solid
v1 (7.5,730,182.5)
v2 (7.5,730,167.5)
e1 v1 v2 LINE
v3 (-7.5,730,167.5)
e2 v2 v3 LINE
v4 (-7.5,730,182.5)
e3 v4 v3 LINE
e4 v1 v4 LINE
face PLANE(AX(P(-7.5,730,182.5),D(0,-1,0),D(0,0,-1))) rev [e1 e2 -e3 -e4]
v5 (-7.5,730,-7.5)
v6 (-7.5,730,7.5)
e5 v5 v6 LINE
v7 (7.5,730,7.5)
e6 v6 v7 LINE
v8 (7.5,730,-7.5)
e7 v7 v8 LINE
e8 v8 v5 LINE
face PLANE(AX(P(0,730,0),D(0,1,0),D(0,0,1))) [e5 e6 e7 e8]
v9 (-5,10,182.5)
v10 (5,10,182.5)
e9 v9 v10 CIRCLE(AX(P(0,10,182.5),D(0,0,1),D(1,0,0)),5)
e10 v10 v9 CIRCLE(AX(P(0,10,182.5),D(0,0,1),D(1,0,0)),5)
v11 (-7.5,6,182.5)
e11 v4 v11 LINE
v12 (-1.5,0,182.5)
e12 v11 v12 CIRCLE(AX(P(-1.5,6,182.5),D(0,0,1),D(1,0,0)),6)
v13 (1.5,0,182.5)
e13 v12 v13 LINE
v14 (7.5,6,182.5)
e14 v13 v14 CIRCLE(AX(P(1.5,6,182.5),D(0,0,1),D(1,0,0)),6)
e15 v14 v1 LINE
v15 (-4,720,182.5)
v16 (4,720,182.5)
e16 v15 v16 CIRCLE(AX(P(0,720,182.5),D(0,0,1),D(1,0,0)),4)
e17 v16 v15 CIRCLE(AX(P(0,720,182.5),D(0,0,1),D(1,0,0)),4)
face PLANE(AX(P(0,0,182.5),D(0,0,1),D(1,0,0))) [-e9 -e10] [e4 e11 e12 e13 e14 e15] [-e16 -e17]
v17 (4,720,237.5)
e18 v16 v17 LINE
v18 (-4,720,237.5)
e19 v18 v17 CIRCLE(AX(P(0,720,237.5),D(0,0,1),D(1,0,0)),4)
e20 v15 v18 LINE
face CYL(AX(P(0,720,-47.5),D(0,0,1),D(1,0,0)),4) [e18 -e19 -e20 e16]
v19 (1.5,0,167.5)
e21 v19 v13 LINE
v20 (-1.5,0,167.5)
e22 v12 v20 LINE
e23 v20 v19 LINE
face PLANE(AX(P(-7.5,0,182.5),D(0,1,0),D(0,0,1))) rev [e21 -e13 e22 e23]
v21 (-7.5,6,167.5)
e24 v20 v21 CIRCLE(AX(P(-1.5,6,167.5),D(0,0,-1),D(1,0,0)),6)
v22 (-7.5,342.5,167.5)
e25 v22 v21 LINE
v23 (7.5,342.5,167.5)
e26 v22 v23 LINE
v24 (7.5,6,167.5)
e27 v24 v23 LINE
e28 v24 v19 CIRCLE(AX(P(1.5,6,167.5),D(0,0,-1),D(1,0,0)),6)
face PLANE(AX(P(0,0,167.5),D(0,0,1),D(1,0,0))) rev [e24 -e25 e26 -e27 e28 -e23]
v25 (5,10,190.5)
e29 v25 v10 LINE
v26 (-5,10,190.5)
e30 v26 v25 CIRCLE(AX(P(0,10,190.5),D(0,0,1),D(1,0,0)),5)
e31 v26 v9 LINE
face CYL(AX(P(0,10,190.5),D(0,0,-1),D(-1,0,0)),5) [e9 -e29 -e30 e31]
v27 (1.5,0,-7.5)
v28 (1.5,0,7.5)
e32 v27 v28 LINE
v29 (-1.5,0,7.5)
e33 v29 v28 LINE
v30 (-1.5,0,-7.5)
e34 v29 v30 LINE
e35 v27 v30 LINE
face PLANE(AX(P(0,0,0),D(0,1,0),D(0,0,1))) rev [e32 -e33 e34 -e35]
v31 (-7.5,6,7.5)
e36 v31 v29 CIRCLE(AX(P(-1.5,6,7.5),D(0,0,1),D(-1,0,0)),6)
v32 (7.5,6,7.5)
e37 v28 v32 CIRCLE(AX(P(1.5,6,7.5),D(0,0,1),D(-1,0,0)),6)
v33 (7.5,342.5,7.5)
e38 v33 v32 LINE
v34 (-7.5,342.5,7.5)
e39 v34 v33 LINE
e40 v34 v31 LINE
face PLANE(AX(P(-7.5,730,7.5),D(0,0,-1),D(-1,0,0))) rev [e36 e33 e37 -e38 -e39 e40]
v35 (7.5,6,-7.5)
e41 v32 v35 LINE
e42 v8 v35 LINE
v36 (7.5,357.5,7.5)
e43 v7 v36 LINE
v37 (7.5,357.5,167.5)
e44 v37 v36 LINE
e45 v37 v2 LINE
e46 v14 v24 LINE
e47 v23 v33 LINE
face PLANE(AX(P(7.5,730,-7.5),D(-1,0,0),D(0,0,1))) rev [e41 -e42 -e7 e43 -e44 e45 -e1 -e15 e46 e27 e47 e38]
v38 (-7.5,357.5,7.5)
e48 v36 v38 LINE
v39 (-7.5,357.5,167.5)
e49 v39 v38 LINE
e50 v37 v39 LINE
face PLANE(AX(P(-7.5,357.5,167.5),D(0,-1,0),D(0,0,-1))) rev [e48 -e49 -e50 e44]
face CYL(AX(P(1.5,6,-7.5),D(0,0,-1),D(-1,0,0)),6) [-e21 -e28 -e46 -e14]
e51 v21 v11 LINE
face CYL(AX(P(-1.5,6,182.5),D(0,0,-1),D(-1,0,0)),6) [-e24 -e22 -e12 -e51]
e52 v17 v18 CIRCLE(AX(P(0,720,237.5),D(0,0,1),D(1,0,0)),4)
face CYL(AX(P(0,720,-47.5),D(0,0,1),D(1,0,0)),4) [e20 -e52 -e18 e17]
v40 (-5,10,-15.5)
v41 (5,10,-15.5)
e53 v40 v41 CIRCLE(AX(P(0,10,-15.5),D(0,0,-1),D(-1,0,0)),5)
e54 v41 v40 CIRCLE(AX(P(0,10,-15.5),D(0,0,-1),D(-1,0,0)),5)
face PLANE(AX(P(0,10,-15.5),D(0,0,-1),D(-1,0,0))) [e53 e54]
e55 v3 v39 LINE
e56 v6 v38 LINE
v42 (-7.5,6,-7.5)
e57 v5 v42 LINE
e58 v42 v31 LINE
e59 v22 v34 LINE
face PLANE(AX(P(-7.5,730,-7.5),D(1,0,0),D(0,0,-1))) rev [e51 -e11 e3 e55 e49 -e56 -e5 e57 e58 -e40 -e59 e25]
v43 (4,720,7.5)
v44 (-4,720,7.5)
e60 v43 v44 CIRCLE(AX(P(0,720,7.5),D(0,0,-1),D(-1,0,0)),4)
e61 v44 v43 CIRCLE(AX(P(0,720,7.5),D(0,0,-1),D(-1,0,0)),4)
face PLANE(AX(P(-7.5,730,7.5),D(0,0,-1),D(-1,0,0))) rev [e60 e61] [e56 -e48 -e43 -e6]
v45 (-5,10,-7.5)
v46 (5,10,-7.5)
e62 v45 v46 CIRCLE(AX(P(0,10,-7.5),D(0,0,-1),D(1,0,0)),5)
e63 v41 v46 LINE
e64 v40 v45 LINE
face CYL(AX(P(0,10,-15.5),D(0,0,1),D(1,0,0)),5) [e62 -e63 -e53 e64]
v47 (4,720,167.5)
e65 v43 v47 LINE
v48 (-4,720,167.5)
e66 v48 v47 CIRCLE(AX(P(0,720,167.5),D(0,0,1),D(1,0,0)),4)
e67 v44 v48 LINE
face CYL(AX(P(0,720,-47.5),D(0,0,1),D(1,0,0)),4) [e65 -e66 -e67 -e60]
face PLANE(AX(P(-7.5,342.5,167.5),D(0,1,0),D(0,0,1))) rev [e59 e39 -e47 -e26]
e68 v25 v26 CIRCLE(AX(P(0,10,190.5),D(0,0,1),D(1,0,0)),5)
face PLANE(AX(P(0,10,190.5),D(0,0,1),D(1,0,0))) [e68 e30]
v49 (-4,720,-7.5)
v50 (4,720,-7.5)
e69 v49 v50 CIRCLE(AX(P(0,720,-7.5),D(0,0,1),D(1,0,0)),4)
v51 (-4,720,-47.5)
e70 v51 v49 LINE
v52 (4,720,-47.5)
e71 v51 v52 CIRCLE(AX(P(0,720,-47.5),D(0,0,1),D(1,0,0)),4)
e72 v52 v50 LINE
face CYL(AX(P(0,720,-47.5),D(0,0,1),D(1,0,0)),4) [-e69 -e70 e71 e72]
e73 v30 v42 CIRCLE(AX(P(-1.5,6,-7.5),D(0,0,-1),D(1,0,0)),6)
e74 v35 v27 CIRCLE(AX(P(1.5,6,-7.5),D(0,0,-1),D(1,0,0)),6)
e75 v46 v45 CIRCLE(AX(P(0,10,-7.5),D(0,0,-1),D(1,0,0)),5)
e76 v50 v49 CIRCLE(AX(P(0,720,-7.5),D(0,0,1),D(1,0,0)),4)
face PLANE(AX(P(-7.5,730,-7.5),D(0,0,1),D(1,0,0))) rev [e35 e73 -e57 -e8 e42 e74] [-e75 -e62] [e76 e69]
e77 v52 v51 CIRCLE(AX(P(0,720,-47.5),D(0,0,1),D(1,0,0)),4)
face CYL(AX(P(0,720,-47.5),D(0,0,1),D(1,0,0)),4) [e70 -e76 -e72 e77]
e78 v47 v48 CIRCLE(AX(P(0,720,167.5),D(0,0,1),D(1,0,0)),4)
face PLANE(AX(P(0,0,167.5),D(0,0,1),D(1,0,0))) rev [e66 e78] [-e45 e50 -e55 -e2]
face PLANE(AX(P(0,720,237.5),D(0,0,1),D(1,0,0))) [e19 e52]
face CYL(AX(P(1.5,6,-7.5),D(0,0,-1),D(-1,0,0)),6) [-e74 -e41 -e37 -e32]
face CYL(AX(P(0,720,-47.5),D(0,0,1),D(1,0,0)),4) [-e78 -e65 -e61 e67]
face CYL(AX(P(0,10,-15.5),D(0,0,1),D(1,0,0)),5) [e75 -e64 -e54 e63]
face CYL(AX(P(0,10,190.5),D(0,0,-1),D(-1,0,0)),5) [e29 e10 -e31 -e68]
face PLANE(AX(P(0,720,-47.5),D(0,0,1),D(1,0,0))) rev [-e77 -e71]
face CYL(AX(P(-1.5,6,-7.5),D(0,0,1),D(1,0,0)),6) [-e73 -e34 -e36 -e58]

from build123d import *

# Parameters (mm, degrees)
SKETCH1_W                = 15
SKETCH1_H                = 15
BOSS_EXTRUDE1_DEPTH      = 730
SKETCH2_R                = 5
BOSS_EXTRUDE2_DEPTH      = 8
SKETCH4_W                = 15
SKETCH4_H                = 15
BOSS_EXTRUDE3_DEPTH      = 160
SKETCH5_W                = 15
SKETCH5_H                = 730
BOSS_EXTRUDE4_DEPTH      = 15
BOSS_EXTRUDE5_START      = 8
SKETCH6_R                = 5
BOSS_EXTRUDE5_DEPTH      = 8
FILLET1_R                = 6
BOSS_EXTRUDE6_DEPTH      = 230
BOSS_EXTRUDE6_DEPTH_BACK = 55
SKETCH7_R                = 4


with BuildPart() as part:
    # Sketch1 → Boss-Extrude1 (new body)
    with BuildSketch(Plane(origin=(0, 0, 0), x_dir=(1, 0, 0), z_dir=(0, 1, 0))):
        Rectangle(SKETCH1_W, SKETCH1_H)
    extrude(amount=BOSS_EXTRUDE1_DEPTH)

    # Sketch2 → Boss-Extrude2 (add)
    with BuildSketch(Plane(origin=(0, 0, -7.5), x_dir=(-1, 0, 0), z_dir=(0, 0, -1))):
        with Locations(Location((0, 10, 0), (0, 0, 180))):
            Circle(SKETCH2_R)
    extrude(amount=BOSS_EXTRUDE2_DEPTH)

    # Sketch4 → Boss-Extrude3 (add)
    with BuildSketch(Plane.XY.offset(7.5)):
        with Locations((0, 350)):
            Rectangle(SKETCH4_W, SKETCH4_H)
    extrude(amount=BOSS_EXTRUDE3_DEPTH)

    # Sketch5 → Boss-Extrude4 (add)
    with BuildSketch(Plane.XY.offset(167.5)):
        with Locations((0, 365)):
            Rectangle(SKETCH5_W, SKETCH5_H)
    extrude(amount=BOSS_EXTRUDE4_DEPTH)

    # Sketch6 → Boss-Extrude5 (add)
    with BuildSketch(Plane.XY.offset(182.5).offset(BOSS_EXTRUDE5_START)):
        with Locations((0, 10)):
            Circle(SKETCH6_R)
    extrude(amount=-BOSS_EXTRUDE5_DEPTH)

    # Fillet1
    fillet1_edges = [part.edges().sort_by_distance(p)[0] for p in [
        (7.5, 0, 175),
        (-7.5, 0, 175),
        (-7.5, 0, 0),
        (7.5, 0, 0),
    ]]
    fillet(fillet1_edges, radius=FILLET1_R)

    # Sketch7 → Boss-Extrude6 (add, two sides: drawn at the far end of the back side and taken through both)
    with BuildSketch(Plane.XY.offset(7.5).offset(-BOSS_EXTRUDE6_DEPTH_BACK)):
        with Locations((0, 720)):
            Circle(SKETCH7_R)
    extrude(amount=BOSS_EXTRUDE6_DEPTH + BOSS_EXTRUDE6_DEPTH_BACK)


solid = part.part
